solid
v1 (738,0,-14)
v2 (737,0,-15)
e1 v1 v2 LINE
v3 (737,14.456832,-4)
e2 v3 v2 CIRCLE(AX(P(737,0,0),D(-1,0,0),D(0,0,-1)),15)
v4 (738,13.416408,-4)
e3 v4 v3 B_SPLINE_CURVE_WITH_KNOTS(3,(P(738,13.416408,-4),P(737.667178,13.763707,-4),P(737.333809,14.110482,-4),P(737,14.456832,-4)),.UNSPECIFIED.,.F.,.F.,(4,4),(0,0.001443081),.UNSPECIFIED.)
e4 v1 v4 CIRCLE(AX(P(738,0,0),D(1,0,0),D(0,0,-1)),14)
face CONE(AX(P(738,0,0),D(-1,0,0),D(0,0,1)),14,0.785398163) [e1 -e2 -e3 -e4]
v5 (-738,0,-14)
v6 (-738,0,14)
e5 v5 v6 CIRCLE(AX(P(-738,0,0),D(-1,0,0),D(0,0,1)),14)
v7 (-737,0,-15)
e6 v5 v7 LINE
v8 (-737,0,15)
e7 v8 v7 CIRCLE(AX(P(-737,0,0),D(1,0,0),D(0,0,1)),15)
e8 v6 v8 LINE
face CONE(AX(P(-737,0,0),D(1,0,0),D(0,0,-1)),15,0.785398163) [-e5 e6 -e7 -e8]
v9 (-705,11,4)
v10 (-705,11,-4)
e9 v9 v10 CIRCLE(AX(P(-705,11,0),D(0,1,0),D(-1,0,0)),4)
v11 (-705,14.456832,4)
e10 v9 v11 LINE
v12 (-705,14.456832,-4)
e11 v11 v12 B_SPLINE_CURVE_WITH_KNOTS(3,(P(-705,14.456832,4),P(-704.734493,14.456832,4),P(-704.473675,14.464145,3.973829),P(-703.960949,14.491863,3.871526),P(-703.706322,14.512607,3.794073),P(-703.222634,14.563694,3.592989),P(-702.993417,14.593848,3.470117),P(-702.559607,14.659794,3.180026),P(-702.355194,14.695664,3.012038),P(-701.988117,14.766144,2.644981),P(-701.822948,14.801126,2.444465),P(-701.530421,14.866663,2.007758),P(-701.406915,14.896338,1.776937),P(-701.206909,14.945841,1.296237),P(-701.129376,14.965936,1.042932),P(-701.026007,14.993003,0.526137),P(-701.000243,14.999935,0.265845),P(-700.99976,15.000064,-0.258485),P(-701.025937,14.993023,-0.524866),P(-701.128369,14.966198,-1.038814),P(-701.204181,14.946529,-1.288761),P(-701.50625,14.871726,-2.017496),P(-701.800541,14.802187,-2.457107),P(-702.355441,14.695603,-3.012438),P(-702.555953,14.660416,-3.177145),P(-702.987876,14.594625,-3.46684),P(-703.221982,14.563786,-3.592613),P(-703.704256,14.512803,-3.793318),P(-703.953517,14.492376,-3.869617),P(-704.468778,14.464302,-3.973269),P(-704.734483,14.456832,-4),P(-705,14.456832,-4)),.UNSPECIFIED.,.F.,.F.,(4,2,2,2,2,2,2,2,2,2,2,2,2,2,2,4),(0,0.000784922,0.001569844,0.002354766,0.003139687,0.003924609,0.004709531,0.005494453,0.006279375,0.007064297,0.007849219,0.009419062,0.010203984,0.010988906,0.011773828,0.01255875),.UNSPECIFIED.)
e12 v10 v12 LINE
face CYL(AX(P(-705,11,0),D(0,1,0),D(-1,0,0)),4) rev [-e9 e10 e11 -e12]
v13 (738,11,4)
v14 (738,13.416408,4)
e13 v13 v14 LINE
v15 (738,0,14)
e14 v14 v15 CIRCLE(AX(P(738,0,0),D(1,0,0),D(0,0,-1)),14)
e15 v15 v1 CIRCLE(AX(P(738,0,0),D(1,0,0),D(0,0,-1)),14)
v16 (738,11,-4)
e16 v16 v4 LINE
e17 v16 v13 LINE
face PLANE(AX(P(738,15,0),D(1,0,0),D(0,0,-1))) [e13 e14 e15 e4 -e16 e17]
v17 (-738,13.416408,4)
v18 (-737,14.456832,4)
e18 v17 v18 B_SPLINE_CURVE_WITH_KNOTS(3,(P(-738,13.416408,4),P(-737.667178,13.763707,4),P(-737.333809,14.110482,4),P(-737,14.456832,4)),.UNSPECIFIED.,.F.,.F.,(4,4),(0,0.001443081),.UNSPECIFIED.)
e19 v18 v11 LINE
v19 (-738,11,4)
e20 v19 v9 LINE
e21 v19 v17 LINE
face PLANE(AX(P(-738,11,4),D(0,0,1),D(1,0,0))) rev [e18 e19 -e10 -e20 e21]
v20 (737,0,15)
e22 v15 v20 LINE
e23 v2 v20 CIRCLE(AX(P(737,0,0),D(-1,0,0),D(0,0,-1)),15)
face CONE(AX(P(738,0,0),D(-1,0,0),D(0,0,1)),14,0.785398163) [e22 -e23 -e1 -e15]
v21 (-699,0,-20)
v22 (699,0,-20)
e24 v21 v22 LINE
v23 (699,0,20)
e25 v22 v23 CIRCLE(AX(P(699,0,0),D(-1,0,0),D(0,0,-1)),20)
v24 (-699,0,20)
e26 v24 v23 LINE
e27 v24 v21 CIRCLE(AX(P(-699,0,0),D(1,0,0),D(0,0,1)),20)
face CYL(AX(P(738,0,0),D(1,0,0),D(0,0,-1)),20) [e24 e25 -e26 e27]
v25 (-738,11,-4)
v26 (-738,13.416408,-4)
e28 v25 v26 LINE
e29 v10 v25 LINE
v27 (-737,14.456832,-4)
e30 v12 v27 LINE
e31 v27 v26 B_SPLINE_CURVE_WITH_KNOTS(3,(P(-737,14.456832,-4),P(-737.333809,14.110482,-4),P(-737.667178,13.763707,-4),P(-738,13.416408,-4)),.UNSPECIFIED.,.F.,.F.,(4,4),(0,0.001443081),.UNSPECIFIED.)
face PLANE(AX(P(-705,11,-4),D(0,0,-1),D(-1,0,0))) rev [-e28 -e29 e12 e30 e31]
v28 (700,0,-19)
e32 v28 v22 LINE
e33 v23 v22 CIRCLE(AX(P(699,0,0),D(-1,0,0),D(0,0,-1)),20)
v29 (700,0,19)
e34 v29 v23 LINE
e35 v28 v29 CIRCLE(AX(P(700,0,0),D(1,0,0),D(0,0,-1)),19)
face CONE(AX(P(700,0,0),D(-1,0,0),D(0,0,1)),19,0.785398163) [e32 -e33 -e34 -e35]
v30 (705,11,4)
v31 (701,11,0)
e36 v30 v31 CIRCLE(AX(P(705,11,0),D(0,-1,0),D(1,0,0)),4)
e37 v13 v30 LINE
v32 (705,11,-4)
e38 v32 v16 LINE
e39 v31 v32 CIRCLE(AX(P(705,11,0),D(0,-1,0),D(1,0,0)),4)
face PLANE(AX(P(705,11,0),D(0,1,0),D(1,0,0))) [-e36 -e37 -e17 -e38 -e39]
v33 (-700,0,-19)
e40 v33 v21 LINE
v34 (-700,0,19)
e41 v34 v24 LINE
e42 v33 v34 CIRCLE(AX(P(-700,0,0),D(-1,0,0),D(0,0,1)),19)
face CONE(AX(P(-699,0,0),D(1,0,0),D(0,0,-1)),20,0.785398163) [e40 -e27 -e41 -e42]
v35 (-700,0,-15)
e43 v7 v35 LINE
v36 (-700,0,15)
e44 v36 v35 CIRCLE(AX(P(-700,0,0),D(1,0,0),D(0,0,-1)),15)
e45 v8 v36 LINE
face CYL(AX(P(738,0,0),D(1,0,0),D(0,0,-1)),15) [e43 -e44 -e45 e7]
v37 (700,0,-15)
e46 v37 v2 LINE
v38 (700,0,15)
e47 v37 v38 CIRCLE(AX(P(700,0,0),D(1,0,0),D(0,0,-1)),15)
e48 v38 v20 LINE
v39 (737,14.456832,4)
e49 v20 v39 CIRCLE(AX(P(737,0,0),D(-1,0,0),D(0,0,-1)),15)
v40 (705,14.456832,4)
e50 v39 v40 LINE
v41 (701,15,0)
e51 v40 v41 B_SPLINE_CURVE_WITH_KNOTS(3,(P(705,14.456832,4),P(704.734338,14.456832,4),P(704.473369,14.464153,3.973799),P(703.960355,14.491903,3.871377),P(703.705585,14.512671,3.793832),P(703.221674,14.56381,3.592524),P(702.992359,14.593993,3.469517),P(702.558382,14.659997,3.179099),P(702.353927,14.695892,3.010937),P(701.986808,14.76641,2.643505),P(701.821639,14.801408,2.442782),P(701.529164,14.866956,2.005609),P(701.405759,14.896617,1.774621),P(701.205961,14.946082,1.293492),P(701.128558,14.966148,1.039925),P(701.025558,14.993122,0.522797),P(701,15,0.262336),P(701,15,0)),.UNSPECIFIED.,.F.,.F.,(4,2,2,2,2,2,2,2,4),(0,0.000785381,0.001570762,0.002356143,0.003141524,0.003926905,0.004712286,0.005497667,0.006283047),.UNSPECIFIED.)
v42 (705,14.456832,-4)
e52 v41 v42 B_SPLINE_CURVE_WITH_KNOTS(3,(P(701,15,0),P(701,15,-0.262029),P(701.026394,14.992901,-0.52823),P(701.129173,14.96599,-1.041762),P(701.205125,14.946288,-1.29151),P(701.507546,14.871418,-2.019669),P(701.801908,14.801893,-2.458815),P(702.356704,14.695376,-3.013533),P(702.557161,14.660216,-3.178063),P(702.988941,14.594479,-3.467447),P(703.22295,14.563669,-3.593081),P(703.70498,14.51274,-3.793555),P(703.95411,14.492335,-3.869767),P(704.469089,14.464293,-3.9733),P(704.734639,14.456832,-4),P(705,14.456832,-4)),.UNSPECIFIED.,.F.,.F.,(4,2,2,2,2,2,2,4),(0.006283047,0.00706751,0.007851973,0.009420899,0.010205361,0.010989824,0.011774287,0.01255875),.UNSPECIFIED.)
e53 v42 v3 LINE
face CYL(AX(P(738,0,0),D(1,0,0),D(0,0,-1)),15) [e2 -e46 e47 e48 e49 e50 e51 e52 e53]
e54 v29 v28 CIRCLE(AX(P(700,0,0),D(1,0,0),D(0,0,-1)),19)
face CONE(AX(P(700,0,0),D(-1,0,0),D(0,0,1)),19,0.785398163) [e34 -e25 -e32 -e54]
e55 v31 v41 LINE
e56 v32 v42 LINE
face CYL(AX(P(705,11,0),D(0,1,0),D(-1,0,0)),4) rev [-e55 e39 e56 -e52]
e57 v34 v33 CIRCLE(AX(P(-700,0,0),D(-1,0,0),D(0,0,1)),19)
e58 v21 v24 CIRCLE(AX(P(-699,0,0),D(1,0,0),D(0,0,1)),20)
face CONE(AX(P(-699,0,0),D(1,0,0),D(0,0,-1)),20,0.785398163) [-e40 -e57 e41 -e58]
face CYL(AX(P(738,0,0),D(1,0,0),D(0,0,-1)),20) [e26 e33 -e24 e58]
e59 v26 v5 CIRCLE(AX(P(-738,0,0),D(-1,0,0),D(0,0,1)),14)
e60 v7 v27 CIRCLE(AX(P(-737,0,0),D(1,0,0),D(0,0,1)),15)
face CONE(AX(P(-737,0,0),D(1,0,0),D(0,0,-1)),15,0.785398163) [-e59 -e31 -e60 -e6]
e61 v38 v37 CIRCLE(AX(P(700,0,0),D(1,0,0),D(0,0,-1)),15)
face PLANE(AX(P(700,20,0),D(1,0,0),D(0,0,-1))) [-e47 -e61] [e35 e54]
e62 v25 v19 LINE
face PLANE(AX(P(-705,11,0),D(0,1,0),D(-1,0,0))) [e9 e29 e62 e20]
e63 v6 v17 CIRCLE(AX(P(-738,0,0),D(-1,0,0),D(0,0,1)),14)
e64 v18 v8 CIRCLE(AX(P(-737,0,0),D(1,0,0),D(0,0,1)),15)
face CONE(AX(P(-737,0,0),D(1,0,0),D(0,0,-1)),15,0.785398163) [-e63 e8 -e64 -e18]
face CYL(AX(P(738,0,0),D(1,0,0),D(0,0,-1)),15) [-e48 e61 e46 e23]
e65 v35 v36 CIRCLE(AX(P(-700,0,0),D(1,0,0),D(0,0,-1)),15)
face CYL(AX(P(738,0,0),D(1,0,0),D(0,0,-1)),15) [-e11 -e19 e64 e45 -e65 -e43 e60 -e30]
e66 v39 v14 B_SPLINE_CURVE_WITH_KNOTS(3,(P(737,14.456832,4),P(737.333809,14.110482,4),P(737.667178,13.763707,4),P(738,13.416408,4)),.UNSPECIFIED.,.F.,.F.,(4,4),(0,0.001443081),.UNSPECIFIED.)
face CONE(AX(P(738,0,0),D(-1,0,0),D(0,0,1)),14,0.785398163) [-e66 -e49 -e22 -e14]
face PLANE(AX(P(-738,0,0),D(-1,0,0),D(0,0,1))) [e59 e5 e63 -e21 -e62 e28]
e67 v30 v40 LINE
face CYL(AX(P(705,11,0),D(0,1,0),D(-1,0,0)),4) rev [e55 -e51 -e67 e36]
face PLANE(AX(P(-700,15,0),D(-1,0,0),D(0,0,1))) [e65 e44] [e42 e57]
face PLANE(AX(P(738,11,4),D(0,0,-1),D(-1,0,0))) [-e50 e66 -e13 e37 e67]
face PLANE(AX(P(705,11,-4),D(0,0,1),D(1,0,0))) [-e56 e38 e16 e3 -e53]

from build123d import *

# Parameters (mm, degrees)
CUT_EXTRUDE1_DEPTH = 4
CHAMFER1_SIZE      = 1


with BuildPart() as part:
    # Sketch1 → Revolve1 (revolve)
    with BuildSketch(Plane.XY, mode=Mode.PRIVATE) as revolve1_sk:
        Polygon((-738, 15), (-700, 15), (-700, 20), (700, 20), (700, 15), (738, 15), (738, 0), (-738, 0), align=None)
    revolve(revolve1_sk.sketch.rotate(Axis((738, 0, 0), (-1, 0, 0)), 90), axis=Axis((738, 0, 0), (-1, 0, 0)))

    # Sketch3 → Cut-Extrude1 (cut)
    with BuildSketch(Plane(origin=(0, 15, 0), x_dir=(1, 0, 0), z_dir=(0, 1, 0))):
        with BuildLine():
            Line((-705, 4), (-738, 4))
            Line((-738, 4), (-738, -4))
            Line((-738, -4), (-705, -4))
            ThreePointArc((-705, -4), (-701, 0), (-705, 4))
        make_face()
    cut_extrude1 = extrude(amount=-CUT_EXTRUDE1_DEPTH, mode=Mode.SUBTRACT)

    # Mirror1: Cut-Extrude1 across plane
    add(cut_extrude1.mirror(Plane.ZY), mode=Mode.SUBTRACT)

    # Chamfer1
    chamfer1_edges = [part.edges().sort_by_distance(p)[0] for p in [
        (-738, -11.937336386, 9.082951062),
        (738, -11.937336386, 9.082951062),
        (700, 0, 20),
        (-700, 0, 20),
    ]]
    chamfer(chamfer1_edges, length=CHAMFER1_SIZE)


solid = part.part
